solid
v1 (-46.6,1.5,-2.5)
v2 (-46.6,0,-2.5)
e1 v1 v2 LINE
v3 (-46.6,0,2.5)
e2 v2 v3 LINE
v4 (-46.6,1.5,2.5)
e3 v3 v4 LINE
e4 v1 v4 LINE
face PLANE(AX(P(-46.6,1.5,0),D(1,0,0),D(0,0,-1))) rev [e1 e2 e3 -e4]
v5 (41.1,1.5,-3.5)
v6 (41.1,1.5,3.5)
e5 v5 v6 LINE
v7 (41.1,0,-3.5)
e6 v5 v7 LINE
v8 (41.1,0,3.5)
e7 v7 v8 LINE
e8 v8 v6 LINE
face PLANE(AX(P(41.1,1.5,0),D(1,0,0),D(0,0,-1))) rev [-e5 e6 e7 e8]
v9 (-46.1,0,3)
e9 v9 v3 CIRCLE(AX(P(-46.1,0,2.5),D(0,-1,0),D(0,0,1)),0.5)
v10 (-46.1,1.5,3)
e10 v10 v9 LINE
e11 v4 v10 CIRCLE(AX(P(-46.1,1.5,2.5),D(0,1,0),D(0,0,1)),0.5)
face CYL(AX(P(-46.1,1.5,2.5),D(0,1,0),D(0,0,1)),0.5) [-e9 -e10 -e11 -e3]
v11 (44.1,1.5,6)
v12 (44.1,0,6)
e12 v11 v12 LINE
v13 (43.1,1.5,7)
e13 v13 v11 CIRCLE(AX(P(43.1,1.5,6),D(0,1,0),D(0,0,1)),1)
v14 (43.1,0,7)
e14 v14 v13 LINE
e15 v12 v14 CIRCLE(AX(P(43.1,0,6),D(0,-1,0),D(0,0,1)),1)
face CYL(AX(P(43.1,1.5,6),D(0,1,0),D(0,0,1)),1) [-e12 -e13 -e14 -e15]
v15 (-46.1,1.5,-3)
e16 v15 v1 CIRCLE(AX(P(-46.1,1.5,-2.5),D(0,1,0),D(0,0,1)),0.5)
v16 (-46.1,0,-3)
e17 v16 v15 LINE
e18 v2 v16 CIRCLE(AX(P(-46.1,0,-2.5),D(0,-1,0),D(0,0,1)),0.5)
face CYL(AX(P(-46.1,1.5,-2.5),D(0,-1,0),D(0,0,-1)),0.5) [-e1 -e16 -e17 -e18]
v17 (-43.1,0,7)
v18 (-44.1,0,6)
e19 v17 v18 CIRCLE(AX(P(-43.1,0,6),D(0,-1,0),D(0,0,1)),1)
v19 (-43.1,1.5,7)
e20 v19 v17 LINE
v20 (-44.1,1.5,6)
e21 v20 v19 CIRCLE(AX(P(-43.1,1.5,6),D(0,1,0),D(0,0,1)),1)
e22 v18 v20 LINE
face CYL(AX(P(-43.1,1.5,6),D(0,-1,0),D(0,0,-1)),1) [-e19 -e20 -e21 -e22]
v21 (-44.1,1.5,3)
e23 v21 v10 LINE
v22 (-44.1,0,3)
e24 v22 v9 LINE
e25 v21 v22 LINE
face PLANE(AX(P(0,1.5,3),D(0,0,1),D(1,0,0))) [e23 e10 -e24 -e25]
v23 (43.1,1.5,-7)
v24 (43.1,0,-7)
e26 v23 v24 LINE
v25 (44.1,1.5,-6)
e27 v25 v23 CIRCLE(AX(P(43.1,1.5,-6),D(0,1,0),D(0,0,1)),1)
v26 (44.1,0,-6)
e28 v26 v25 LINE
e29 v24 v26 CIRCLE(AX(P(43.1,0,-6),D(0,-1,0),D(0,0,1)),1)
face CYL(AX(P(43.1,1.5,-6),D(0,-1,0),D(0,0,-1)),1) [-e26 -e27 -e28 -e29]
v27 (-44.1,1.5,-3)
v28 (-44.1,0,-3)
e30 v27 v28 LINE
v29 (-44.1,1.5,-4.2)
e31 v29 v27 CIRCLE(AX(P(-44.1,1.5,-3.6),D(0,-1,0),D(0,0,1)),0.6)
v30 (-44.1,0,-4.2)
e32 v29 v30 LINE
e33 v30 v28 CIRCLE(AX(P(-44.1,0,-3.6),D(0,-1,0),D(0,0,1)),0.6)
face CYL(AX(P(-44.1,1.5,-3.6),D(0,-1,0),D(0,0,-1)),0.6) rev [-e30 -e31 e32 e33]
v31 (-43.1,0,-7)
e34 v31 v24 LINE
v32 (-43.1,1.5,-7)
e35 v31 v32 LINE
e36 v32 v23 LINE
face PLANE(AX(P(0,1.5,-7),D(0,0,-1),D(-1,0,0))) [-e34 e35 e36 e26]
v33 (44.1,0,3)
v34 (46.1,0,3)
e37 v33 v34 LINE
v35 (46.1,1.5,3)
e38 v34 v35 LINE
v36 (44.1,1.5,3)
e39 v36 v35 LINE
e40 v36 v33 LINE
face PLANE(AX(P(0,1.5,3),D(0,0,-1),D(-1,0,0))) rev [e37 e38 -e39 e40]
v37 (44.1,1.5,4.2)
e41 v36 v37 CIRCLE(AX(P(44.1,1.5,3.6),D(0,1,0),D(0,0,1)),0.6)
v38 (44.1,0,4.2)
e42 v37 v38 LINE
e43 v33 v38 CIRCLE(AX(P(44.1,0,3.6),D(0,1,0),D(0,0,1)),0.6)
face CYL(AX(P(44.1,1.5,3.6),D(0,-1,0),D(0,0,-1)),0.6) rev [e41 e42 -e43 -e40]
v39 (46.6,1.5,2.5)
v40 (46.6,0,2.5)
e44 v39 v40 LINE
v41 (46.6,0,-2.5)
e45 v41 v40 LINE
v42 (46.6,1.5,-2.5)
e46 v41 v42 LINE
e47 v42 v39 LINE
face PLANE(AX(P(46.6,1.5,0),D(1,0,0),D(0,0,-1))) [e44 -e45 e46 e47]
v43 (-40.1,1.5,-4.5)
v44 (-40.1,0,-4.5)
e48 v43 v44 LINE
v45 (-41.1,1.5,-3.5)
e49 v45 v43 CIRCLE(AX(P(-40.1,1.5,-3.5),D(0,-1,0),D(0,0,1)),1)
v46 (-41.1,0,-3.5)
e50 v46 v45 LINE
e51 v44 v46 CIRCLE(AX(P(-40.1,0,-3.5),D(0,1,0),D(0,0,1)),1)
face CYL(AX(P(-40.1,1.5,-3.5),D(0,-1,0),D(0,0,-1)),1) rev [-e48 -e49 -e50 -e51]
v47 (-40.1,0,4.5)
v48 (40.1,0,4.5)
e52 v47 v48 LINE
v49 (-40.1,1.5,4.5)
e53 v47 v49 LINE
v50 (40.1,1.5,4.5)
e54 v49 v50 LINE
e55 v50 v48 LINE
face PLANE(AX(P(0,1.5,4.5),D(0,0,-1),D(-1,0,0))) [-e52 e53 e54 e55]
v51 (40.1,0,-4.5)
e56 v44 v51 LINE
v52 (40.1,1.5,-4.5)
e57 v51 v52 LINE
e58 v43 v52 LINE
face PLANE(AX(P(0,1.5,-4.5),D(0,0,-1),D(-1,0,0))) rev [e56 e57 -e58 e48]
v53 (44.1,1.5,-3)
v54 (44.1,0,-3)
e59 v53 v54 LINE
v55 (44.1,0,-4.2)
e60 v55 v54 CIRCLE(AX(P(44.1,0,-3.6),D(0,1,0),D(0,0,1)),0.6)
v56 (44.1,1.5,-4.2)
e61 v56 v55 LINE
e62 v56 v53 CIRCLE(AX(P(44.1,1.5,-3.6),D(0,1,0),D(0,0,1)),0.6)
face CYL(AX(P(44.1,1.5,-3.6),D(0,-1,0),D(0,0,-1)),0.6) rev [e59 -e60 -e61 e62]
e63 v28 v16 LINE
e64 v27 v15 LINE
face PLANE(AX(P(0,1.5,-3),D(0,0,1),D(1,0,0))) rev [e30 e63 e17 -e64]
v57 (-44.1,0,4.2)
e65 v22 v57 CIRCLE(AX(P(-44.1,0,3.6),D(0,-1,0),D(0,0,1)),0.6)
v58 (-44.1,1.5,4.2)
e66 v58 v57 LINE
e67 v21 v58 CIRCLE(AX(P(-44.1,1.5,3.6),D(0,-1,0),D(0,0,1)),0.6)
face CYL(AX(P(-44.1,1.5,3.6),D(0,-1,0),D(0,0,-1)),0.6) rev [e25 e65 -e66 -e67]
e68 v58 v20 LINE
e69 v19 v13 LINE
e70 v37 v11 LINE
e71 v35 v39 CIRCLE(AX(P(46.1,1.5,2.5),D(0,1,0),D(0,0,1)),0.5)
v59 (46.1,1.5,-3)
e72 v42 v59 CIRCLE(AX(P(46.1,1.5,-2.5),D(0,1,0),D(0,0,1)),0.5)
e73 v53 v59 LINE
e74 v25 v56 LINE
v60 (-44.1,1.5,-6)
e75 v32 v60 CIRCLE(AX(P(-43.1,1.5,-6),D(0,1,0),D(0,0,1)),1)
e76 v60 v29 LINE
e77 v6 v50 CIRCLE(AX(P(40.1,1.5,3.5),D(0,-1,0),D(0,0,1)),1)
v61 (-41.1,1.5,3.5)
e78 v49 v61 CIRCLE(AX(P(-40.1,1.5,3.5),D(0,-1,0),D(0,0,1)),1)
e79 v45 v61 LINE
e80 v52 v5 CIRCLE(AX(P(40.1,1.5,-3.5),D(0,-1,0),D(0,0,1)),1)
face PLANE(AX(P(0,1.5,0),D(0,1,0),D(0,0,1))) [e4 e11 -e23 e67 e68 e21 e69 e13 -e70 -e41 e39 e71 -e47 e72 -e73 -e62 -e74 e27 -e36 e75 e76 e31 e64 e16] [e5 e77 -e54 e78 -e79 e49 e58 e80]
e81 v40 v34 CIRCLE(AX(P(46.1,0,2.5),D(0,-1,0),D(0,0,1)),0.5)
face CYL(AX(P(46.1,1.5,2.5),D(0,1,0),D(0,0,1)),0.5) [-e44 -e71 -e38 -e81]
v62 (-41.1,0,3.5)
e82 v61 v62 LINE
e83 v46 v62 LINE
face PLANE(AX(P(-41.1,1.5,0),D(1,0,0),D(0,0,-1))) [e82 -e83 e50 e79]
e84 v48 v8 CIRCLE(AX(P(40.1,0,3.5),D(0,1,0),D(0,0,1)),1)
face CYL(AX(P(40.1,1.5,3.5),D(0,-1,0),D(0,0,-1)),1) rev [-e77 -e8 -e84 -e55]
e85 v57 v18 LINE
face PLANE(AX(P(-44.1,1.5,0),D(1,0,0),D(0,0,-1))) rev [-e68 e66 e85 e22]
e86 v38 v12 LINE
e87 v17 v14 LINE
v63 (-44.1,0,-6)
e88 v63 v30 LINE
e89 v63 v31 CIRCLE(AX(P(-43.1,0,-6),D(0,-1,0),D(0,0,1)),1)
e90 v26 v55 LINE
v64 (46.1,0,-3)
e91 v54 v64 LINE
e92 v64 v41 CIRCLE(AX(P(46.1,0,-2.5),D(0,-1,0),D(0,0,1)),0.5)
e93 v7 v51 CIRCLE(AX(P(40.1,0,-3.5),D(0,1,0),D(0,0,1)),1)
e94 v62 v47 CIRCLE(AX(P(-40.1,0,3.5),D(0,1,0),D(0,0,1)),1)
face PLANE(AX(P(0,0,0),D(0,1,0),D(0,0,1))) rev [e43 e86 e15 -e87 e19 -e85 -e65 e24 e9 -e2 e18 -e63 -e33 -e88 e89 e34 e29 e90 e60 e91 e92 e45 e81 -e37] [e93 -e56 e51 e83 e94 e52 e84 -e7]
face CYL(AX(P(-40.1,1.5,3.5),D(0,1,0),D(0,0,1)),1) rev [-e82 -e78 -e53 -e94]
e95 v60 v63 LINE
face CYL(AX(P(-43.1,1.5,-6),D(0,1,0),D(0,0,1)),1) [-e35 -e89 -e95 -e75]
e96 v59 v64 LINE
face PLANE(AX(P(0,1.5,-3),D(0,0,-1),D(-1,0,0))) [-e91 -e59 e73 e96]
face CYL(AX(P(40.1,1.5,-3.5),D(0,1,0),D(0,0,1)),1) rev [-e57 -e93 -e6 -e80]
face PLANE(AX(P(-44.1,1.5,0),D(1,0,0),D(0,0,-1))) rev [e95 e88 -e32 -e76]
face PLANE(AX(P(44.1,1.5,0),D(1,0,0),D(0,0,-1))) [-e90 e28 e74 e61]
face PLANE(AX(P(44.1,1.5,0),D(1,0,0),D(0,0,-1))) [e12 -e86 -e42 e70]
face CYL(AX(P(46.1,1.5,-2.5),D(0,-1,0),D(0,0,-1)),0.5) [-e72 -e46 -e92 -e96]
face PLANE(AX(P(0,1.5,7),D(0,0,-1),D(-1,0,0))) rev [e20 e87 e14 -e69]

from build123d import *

# Parameters (mm, degrees)
SKETCH_1_W      = 82.2
SKETCH_1_H      = 9
EXTRUDE_1_DEPTH = 1.5
FILLET_1_R      = 0.5
FILLET_2_R      = 1


with BuildPart() as part:
    # 草图1 → 凸台-拉伸1 (new body)
    with BuildSketch(Plane(origin=(0, 0, 0), x_dir=(1, 0, 0), z_dir=(0, 1, 0))):
        with BuildLine():
            Line((44.1, 7), (-44.1, 7))
            Line((-44.1, 7), (-44.1, 4.2))
            ThreePointArc((-44.1, 4.2), (-43.5, 3.6), (-44.1, 3))
            Line((-44.1, 3), (-46.6, 3))
            Line((-46.6, 3), (-46.6, -3))
            Line((-46.6, -3), (-44.1, -3))
            ThreePointArc((-44.1, -3), (-43.5, -3.6), (-44.1, -4.2))
            Line((-44.1, -4.2), (-44.1, -7))
            Line((-44.1, -7), (44.1, -7))
            Line((44.1, -7), (44.1, -4.2))
            ThreePointArc((44.1, -4.2), (43.5, -3.6), (44.1, -3))
            Line((44.1, -3), (46.6, -3))
            Line((46.6, -3), (46.6, 3))
            Line((46.6, 3), (44.1, 3))
            ThreePointArc((44.1, 3), (43.5, 3.6), (44.1, 4.2))
            Line((44.1, 4.2), (44.1, 7))
        make_face()
        Rectangle(SKETCH_1_W, SKETCH_1_H, mode=Mode.SUBTRACT)
    extrude(amount=EXTRUDE_1_DEPTH)

    # 圆角1
    fillet_1_edges = [part.edges().sort_by_distance(p)[0] for p in [
        (46.6, 0.75, -3),
        (46.6, 0.75, 3),
        (-46.6, 0.75, 3),
        (-46.6, 0.75, -3),
    ]]
    fillet(fillet_1_edges, radius=FILLET_1_R)

    # 圆角2
    fillet_2_edges = [part.edges().sort_by_distance(p)[0] for p in [
        (-44.1, 0.75, -7),
        (44.1, 0.75, -7),
        (44.1, 0.75, 7),
        (-44.1, 0.75, 7),
        (-41.1, 0.75, -4.5),
        (-41.1, 0.75, 4.5),
        (41.1, 0.75, 4.5),
        (41.1, 0.75, -4.5),
    ]]
    fillet(fillet_2_edges, radius=FILLET_2_R)


solid = part.part
